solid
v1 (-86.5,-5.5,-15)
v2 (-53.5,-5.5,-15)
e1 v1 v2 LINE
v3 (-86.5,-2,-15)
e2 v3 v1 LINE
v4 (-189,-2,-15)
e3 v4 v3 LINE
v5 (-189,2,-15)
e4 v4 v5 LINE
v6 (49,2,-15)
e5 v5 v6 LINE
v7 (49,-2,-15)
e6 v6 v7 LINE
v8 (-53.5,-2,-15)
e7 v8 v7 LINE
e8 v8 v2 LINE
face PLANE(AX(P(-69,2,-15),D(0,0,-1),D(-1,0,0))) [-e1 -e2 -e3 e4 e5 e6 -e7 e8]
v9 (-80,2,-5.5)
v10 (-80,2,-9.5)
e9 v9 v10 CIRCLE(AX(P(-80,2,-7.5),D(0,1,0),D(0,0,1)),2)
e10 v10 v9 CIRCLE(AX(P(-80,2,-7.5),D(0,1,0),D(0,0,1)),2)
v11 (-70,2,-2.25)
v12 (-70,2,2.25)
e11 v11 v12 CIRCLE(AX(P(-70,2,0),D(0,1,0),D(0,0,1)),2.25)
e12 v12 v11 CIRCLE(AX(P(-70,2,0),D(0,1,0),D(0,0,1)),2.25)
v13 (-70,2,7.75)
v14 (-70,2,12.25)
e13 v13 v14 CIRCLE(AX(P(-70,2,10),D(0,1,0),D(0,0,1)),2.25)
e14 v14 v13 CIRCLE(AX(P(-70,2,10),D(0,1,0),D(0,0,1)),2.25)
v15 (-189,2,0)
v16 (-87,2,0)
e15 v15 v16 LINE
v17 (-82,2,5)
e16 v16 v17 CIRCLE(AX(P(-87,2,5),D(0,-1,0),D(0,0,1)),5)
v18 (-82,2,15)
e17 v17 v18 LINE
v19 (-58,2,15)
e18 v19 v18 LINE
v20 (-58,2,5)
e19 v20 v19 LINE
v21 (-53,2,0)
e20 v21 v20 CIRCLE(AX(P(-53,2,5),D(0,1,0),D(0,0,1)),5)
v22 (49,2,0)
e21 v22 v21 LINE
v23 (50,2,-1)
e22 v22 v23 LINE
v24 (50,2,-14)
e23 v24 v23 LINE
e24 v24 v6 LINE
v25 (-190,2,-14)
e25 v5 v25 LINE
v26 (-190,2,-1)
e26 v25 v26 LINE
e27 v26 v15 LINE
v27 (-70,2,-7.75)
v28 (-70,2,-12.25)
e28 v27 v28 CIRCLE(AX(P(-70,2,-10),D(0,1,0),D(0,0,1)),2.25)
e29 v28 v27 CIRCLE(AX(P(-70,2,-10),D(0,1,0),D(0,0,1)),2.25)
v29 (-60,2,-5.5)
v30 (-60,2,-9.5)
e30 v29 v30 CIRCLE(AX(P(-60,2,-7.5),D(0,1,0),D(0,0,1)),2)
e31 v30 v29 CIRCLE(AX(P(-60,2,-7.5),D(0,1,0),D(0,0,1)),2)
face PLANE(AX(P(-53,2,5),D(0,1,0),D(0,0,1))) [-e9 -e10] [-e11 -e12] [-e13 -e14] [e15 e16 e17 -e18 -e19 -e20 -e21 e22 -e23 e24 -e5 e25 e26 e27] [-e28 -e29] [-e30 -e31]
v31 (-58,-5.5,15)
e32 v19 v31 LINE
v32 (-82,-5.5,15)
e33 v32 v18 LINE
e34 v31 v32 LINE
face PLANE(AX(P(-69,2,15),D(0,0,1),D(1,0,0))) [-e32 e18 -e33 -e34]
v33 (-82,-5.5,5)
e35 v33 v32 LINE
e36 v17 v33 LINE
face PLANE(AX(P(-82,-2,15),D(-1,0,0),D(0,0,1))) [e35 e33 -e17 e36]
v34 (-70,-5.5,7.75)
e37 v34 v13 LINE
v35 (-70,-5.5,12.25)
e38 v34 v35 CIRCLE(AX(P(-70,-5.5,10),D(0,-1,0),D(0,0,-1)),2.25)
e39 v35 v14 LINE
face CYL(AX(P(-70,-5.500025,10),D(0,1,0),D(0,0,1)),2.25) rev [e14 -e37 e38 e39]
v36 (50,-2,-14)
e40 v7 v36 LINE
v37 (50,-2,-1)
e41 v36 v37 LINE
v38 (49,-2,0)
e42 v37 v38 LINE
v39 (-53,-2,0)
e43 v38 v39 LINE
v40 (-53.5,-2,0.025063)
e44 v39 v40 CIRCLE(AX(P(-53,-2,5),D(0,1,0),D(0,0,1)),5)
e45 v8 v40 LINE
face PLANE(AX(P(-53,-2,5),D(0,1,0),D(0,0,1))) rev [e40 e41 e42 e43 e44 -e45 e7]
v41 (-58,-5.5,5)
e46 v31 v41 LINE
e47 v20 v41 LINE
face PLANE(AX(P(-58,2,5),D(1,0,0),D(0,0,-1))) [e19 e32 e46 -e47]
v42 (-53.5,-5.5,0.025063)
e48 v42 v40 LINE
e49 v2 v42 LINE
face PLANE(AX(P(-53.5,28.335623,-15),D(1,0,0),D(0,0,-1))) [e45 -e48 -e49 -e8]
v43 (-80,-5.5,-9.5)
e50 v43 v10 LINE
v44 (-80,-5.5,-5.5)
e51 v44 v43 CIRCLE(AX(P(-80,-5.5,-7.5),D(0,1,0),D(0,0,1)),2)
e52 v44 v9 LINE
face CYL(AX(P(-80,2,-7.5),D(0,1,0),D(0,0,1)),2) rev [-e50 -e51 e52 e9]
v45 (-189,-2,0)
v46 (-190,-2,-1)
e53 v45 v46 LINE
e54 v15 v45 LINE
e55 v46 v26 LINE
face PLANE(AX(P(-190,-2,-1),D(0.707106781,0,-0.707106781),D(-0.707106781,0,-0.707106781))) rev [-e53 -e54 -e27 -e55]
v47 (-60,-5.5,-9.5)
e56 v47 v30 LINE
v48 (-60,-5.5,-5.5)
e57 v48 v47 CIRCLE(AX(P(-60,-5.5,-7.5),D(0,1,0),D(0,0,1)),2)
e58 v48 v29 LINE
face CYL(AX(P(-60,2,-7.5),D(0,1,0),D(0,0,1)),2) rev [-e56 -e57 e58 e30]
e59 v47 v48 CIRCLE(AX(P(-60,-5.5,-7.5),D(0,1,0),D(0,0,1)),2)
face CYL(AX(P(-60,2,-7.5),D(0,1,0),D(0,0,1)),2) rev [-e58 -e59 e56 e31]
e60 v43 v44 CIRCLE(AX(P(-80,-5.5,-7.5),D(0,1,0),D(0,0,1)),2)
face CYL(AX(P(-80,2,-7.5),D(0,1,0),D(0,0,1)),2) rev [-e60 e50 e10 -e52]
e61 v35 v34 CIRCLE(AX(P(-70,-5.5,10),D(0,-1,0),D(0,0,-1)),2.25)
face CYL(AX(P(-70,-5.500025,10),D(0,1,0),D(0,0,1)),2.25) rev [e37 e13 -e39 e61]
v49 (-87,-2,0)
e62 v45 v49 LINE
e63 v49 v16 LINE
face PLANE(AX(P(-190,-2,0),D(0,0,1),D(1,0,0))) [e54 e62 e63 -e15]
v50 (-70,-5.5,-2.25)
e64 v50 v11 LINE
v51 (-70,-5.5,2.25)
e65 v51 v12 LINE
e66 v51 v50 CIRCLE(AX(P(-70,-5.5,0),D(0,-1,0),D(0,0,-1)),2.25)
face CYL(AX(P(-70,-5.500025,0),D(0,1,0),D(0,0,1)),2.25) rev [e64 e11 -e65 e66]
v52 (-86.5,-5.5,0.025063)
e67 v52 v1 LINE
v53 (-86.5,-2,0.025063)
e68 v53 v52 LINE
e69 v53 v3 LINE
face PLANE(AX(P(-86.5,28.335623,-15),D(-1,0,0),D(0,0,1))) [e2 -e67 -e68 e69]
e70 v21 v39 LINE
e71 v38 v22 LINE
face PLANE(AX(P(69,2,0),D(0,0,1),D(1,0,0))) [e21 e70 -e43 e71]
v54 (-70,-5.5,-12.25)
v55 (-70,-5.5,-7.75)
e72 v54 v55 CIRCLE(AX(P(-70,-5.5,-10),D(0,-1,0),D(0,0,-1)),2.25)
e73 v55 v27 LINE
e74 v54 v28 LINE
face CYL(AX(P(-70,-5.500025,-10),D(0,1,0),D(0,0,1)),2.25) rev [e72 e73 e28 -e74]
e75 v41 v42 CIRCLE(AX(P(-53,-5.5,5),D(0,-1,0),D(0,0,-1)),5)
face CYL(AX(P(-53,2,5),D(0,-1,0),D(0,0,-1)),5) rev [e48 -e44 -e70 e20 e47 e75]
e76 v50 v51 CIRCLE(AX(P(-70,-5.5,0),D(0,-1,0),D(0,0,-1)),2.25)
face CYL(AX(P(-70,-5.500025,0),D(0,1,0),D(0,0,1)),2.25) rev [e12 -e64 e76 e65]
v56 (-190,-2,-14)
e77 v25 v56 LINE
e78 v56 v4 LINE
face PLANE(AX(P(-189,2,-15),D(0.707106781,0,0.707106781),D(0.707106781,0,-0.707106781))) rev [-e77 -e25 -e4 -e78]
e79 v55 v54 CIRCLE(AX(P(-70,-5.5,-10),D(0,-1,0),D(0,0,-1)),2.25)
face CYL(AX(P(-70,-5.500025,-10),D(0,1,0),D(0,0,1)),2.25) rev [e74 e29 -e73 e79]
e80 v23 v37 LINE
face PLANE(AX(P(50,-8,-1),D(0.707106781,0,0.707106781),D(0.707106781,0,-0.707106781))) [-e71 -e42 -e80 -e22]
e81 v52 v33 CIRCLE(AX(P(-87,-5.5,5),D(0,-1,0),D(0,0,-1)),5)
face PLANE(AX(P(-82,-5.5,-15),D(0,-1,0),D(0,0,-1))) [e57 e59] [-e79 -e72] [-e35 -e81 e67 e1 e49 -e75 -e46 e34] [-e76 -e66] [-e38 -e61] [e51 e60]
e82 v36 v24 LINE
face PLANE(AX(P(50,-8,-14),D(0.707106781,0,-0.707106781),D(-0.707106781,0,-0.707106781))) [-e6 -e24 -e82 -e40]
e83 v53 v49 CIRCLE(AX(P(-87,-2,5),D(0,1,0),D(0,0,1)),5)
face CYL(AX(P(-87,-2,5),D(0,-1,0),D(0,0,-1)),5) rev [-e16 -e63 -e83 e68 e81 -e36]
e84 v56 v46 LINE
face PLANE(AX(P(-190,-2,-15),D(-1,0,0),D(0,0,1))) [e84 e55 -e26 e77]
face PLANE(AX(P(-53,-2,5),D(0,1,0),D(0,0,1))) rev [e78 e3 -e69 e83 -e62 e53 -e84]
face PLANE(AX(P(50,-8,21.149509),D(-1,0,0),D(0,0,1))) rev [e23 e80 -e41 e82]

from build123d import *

# Parameters (mm, degrees)
BOSS_EXTRUDE_1_DEPTH   = 4
BOSS_EXTRUDE_2_DEPTH   = 4
FILLET_1_R             = 5
SKETCH_6_W             = 24
SKETCH_6_H             = 30
BOSS_EXTRUDE_3_DEPTH   = 3.5
SKETCH_3_R             = 2.25
CUT_EXTRUDE_1_DEPTH    = 191.738695602
LINEAR_PATTERN_1_COUNT = 3
LINEAR_PATTERN_1_PITCH = 10
SKETCH_7_W             = 63.778369094
SKETCH_7_H             = 56.242484603
CUT_EXTRUDE_2_DEPTH    = 10
CHAMFER_3_SIZE         = 1
SKETCH_8_W             = 4.5
SKETCH_8_H             = 30
BOSS_EXTRUDE_4_DEPTH   = 3.5
CUT_EXTRUDE_START      = -10
CUT_EXTRUDE_3_DEPTH    = 10
F_4_0_4_HOLE_1_D       = 4
LINEAR_PATTERN_2_COUNT = 2
LINEAR_PATTERN_2_PITCH = 20


with BuildPart() as part:
    # Sketch 1 → Boss-Extrude 1 (new body)
    with BuildSketch(Plane.XZ.offset(2)):
        with BuildLine():
            Line((-59, 15), (-69, 15))
            Line((-69, 15), (-70, 15))
            Line((-70, 15), (-70, -15))
            Line((-70, -15), (-69, -15))
            Line((-69, -15), (69, -15))
            Line((69, -15), (70, -14))
            Line((70, -14), (70, -1))
            Line((70, -1), (69, 0))
            Line((69, 0), (-53, 0))
            ThreePointArc((-53, 0), (-56.535533906, 1.464466094), (-58, 5))
            Line((-58, 5), (-58, 15))
            Line((-58, 15), (-59, 15))
        make_face()
    extrude(amount=-BOSS_EXTRUDE_1_DEPTH)

    # Sketch 2 → Boss-Extrude 2 (add)
    with BuildSketch(Plane(origin=(0, 2, 0), x_dir=(1, 0, 0), z_dir=(0, 1, 0))):
        Polygon((-70, 15), (-190, 15), (-190, 0), (-82, 0), (-82, -15), (-70, -15), align=None)
    extrude(amount=-BOSS_EXTRUDE_2_DEPTH)

    # Fillet 1
    fillet_1_edges = [part.edges().sort_by_distance(p)[0] for p in [
        (-82, 0, 0),
    ]]
    fillet(fillet_1_edges, radius=FILLET_1_R)

    # Sketch 6 → Boss-Extrude 3 (add)
    with BuildSketch(Plane.XZ.offset(2)):
        with Locations((-70, 0)):
            Rectangle(SKETCH_6_W, SKETCH_6_H)
    extrude(amount=BOSS_EXTRUDE_3_DEPTH)

    # Sketch 3 → Cut-Extrude 1 (cut, through all)
    with BuildSketch(Plane(origin=(0, 2, 0), x_dir=(1, 0, 0), z_dir=(0, 1, 0))):
        with Locations(Location((-70, -10, 0), (0, 0, 270))):
            Circle(SKETCH_3_R)
    cut_extrude_1 = extrude(amount=-CUT_EXTRUDE_1_DEPTH, mode=Mode.SUBTRACT)

    # Linear Pattern 1: Cut-Extrude 1 ×3
    with Locations(*[(0, 0, -i * LINEAR_PATTERN_1_PITCH) for i in range(1, LINEAR_PATTERN_1_COUNT)]):
        add(cut_extrude_1, mode=Mode.SUBTRACT)

    # Sketch 7 → Cut-Extrude 2 (cut)
    with BuildSketch(Plane(origin=(0, 2, 0), x_dir=(1, 0, 0), z_dir=(0, 1, 0))):
        with Locations((81.889184547, 6.971733155)):
            Rectangle(SKETCH_7_W, SKETCH_7_H)
    extrude(amount=-CUT_EXTRUDE_2_DEPTH, mode=Mode.SUBTRACT)

    # Chamfer 3
    chamfer_3_edges = [part.edges().sort_by_distance(p)[0] for p in [
        (50, 0, -15),
        (50, 0, 0),
        (-190, 0, -15),
        (-190, 0, 0),
    ]]
    chamfer(chamfer_3_edges, length=CHAMFER_3_SIZE)

    # Sketch 8 → Boss-Extrude 4 (add)
    with BuildSketch(Plane.XZ.offset(5.5)):
        with Locations((-55.75, 0)):
            Rectangle(SKETCH_8_W, SKETCH_8_H)
        with Locations((-84.25, 0)):
            Rectangle(SKETCH_8_W, SKETCH_8_H)
    extrude(amount=-BOSS_EXTRUDE_4_DEPTH)

    # Sketch 9 → Cut-Extrude 3 (cut)
    with BuildSketch(Plane(origin=(0, -2, 0), x_dir=(1, 0, 0), z_dir=(0, 1, 0)).offset(CUT_EXTRUDE_START)):
        with BuildLine():
            Line((-53.5, -15), (-58, -15))
            Line((-58, -15), (-58, -5))
            ThreePointArc((-58, -5), (-56.708099244, -1.645898034), (-53.5, -0.025062814))
            Line((-53.5, -0.025062814), (-53.5, -15))
        make_face()
        with BuildLine():
            Line((-82, -15), (-86.5, -15))
            Line((-86.5, -15), (-86.5, -0.025062814))
            ThreePointArc((-86.5, -0.025062814), (-83.291900756, -1.645898034), (-82, -5))
            Line((-82, -5), (-82, -15))
        make_face()
    extrude(amount=CUT_EXTRUDE_3_DEPTH, mode=Mode.SUBTRACT)

    # Ø4.0 (4) Hole 1 (through all)
    with Locations(Plane(origin=(0, 2, 0), x_dir=(-1, 0, 0), z_dir=(0, 1, 0))):
        with Locations((60, -7.5)):
            f_4_0_4_hole_1 = Hole(F_4_0_4_HOLE_1_D / 2)

    # Linear Pattern 2: Ø4.0 (4) Hole 1 ×2
    with Locations(*[(-i * LINEAR_PATTERN_2_PITCH, 0, 0) for i in range(1, LINEAR_PATTERN_2_COUNT)]):
        add(f_4_0_4_hole_1, mode=Mode.SUBTRACT)


solid = part.part
